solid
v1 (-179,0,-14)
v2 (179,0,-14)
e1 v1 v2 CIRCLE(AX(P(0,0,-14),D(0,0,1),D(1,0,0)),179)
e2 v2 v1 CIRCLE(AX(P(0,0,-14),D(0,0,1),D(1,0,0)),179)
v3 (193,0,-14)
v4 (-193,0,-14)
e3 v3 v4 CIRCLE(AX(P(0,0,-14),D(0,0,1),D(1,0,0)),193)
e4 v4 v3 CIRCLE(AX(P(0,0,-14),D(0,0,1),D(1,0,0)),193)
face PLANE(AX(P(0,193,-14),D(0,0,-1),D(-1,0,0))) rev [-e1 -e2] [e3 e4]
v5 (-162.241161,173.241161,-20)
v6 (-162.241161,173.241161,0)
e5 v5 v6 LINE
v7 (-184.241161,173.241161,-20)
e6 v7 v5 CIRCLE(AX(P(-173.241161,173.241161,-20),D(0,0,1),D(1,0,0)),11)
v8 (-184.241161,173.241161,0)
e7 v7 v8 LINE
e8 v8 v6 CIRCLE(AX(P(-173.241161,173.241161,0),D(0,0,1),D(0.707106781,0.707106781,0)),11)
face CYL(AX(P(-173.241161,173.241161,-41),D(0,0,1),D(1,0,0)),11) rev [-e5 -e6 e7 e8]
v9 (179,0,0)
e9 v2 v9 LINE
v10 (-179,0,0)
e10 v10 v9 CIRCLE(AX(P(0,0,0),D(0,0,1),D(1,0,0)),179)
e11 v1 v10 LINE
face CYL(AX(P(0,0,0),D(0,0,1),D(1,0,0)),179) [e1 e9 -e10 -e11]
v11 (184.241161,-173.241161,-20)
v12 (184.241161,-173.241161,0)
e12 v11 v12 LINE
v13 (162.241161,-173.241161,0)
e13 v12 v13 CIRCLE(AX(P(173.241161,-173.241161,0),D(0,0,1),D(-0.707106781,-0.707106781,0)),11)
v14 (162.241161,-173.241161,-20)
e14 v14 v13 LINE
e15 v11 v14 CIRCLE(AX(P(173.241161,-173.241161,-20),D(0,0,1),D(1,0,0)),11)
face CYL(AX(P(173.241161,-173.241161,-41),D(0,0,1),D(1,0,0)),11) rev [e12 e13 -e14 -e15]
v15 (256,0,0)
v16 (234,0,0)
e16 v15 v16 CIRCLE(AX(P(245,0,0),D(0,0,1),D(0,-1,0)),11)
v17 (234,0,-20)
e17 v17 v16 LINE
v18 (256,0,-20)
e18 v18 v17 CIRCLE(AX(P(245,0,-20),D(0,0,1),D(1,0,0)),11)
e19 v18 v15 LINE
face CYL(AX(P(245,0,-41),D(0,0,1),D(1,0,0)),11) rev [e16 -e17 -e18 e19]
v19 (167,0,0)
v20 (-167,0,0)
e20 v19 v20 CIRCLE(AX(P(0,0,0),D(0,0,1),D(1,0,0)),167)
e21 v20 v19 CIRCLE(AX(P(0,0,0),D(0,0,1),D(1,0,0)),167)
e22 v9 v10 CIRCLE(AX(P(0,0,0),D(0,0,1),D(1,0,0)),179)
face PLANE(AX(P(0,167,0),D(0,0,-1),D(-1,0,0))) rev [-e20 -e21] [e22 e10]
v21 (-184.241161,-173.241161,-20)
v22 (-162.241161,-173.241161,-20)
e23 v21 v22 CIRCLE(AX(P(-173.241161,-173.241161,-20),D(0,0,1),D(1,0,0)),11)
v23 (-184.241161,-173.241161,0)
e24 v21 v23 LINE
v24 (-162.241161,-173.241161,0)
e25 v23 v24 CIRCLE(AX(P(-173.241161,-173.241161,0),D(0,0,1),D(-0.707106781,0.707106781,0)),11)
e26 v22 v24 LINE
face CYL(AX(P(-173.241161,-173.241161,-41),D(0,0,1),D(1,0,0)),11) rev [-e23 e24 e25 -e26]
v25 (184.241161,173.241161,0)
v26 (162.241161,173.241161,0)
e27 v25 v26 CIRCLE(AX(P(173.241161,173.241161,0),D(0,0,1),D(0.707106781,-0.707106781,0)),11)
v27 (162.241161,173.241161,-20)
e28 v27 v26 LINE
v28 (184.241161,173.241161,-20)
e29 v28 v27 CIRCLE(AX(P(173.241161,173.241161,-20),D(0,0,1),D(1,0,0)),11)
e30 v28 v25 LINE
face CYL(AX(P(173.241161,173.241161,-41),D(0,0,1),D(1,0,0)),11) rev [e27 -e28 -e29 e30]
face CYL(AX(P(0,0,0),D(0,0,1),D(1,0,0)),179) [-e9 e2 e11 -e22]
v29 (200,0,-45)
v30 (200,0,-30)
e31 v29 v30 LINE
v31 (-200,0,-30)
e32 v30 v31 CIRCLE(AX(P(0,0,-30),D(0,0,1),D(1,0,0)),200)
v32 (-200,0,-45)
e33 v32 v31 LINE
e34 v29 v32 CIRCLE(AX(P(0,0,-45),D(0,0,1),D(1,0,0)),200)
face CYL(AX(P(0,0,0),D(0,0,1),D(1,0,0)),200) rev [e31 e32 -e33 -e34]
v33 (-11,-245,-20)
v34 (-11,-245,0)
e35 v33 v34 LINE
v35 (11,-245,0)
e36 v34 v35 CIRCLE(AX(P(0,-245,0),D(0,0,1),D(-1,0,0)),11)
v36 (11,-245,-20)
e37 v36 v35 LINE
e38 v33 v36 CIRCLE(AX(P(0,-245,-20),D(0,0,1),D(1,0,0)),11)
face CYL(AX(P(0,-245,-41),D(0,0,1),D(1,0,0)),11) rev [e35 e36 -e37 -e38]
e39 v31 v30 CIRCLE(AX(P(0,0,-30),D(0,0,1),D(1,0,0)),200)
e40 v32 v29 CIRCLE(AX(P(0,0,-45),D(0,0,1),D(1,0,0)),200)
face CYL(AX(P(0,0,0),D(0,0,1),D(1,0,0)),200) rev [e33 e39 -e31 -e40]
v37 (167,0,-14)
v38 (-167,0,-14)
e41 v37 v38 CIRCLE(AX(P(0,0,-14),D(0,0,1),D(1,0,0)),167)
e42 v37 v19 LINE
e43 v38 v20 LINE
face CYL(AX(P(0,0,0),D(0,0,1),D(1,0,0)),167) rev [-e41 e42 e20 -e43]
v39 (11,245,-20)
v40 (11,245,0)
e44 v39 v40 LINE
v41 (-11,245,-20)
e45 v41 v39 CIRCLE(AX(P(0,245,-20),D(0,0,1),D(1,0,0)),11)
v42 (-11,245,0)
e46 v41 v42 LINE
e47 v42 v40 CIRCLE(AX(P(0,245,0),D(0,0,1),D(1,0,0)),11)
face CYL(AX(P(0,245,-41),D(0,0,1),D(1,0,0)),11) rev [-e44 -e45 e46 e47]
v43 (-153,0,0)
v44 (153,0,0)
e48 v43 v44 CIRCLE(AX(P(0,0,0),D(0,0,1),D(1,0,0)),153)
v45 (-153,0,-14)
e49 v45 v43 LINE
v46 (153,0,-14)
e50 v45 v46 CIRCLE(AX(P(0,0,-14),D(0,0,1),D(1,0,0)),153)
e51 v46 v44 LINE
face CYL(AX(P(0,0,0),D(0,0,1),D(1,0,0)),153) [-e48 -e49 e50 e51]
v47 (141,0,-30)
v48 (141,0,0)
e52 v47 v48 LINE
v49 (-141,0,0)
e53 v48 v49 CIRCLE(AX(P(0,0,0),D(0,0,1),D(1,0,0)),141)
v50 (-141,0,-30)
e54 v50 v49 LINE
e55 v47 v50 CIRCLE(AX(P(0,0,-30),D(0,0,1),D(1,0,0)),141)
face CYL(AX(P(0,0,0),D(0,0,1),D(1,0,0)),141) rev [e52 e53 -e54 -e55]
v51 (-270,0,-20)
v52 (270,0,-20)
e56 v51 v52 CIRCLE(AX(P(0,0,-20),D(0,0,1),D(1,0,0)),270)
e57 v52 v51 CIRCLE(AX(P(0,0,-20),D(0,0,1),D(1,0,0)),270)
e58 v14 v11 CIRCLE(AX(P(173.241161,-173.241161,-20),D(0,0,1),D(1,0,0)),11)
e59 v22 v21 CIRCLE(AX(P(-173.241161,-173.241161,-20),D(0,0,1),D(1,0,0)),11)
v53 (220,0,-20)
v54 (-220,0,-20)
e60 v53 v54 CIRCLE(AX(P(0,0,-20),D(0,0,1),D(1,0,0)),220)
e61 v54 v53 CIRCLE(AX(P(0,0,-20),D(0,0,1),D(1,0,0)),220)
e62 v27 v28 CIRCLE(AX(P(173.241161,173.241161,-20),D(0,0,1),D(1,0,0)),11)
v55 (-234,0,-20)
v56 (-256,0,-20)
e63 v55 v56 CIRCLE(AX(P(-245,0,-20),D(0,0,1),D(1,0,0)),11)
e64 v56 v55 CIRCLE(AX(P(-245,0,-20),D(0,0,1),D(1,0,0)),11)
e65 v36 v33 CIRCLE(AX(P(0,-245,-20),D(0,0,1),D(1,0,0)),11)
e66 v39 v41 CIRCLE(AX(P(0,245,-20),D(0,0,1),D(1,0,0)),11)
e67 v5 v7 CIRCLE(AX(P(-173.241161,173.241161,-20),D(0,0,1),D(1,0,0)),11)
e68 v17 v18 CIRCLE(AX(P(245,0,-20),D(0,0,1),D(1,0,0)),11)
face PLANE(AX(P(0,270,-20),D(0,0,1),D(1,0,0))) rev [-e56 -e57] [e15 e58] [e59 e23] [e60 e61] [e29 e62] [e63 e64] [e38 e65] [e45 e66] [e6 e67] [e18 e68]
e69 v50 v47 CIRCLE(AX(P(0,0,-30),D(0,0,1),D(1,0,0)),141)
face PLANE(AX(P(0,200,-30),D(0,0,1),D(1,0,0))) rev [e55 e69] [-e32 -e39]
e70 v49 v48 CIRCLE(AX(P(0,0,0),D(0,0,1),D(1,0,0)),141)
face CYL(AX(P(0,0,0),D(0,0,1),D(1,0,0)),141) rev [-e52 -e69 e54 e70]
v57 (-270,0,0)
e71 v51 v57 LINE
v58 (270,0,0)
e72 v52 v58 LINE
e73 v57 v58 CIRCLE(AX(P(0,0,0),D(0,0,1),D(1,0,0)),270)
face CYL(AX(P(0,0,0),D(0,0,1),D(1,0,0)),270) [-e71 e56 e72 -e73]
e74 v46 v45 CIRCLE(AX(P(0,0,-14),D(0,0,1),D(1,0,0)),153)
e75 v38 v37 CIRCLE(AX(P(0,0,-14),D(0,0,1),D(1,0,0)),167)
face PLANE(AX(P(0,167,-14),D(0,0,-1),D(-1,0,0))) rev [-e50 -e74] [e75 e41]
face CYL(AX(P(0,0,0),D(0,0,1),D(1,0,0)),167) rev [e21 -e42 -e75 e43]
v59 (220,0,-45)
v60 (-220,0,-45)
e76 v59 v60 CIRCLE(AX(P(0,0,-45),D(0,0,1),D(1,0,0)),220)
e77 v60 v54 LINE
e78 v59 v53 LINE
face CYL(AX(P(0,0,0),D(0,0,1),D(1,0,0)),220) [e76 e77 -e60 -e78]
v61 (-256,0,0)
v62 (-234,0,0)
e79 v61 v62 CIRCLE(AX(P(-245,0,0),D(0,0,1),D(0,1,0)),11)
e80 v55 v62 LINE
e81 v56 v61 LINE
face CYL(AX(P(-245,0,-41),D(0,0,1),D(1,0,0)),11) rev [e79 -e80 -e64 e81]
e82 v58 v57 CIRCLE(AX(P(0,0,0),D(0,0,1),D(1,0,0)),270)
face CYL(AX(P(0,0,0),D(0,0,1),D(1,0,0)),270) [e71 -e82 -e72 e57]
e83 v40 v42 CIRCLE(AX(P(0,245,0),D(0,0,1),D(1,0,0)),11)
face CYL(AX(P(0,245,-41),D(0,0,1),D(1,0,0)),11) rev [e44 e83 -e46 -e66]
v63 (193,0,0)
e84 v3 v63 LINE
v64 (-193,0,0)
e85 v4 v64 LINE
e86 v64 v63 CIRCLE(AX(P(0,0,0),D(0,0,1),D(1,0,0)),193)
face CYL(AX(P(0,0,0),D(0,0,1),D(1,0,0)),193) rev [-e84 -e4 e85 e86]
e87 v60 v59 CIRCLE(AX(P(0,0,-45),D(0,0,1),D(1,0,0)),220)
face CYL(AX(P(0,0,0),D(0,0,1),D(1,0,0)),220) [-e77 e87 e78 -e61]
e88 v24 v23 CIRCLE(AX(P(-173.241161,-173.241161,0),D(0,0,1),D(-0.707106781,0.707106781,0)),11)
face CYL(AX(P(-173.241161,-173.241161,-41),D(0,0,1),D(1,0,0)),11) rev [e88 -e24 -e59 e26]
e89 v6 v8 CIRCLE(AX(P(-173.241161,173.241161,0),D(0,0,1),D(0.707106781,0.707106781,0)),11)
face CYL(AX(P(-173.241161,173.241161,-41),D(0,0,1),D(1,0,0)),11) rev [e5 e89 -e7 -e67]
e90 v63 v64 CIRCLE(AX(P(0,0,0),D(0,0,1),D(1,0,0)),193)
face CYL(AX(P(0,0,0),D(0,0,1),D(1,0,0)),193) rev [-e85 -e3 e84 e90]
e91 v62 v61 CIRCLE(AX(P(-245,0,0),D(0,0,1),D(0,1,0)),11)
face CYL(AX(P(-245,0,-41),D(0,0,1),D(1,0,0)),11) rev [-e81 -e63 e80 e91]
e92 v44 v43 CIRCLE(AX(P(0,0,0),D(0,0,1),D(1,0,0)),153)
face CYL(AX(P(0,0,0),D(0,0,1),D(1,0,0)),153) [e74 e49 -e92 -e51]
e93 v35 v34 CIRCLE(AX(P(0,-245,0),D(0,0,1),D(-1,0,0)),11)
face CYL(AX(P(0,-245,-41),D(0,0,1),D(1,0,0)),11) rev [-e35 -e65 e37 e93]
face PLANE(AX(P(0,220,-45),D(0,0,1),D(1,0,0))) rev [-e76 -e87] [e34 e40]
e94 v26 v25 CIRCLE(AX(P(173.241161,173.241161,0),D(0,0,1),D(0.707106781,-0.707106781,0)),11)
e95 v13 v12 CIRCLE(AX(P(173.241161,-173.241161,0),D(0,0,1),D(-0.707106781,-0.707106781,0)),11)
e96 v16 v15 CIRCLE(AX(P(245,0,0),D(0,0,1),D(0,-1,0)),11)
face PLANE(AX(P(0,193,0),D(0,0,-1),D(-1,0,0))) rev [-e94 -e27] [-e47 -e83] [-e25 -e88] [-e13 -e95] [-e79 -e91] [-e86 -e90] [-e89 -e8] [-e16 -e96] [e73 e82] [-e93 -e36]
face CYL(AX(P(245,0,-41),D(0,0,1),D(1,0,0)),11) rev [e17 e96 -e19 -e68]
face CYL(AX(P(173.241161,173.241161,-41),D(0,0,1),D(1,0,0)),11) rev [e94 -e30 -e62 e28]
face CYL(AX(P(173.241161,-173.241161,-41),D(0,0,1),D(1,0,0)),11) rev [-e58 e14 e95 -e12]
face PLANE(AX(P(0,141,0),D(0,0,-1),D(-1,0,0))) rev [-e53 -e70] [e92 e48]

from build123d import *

# Parameters (mm, degrees)
SKETCH2_R          = 11
CUT_EXTRUDE1_DEPTH = 41
CIRPATTERN1_COUNT  = 8


with BuildPart() as part:
    # Sketch1 → Revolve1 (revolve)
    with BuildSketch(Plane(origin=(0, 0, 0), x_dir=(0, 0, -1), z_dir=(1, 0, 0)), mode=Mode.PRIVATE) as revolve1_sk:
        Polygon((0, 141), (0, 153), (14, 153), (14, 167), (0, 167), (0, 179), (14, 179), (14, 193), (0, 193), (0, 270), (20, 270), (20, 220), (45, 220), (45, 200), (30, 200), (30, 141), align=None)
    revolve(revolve1_sk.sketch.rotate(Axis((0, 0, 0), (0, 0, -1)), 90), axis=Axis((0, 0, 0), (0, 0, -1)))

    # Sketch2 → Cut-Extrude1 (cut)
    with BuildSketch(Plane.XY):
        with Locations((0, 245)):
            Circle(SKETCH2_R)
    cut_extrude1 = extrude(amount=-CUT_EXTRUDE1_DEPTH, mode=Mode.SUBTRACT)

    # CirPattern1: Cut-Extrude1 ×8 about axis
    cirpattern1_axis = Axis((0, 0, 0), (0, 0, 1))
    for i in range(1, CIRPATTERN1_COUNT):
        add(cut_extrude1.rotate(cirpattern1_axis, i * 360 / CIRPATTERN1_COUNT), mode=Mode.SUBTRACT)


solid = part.part
